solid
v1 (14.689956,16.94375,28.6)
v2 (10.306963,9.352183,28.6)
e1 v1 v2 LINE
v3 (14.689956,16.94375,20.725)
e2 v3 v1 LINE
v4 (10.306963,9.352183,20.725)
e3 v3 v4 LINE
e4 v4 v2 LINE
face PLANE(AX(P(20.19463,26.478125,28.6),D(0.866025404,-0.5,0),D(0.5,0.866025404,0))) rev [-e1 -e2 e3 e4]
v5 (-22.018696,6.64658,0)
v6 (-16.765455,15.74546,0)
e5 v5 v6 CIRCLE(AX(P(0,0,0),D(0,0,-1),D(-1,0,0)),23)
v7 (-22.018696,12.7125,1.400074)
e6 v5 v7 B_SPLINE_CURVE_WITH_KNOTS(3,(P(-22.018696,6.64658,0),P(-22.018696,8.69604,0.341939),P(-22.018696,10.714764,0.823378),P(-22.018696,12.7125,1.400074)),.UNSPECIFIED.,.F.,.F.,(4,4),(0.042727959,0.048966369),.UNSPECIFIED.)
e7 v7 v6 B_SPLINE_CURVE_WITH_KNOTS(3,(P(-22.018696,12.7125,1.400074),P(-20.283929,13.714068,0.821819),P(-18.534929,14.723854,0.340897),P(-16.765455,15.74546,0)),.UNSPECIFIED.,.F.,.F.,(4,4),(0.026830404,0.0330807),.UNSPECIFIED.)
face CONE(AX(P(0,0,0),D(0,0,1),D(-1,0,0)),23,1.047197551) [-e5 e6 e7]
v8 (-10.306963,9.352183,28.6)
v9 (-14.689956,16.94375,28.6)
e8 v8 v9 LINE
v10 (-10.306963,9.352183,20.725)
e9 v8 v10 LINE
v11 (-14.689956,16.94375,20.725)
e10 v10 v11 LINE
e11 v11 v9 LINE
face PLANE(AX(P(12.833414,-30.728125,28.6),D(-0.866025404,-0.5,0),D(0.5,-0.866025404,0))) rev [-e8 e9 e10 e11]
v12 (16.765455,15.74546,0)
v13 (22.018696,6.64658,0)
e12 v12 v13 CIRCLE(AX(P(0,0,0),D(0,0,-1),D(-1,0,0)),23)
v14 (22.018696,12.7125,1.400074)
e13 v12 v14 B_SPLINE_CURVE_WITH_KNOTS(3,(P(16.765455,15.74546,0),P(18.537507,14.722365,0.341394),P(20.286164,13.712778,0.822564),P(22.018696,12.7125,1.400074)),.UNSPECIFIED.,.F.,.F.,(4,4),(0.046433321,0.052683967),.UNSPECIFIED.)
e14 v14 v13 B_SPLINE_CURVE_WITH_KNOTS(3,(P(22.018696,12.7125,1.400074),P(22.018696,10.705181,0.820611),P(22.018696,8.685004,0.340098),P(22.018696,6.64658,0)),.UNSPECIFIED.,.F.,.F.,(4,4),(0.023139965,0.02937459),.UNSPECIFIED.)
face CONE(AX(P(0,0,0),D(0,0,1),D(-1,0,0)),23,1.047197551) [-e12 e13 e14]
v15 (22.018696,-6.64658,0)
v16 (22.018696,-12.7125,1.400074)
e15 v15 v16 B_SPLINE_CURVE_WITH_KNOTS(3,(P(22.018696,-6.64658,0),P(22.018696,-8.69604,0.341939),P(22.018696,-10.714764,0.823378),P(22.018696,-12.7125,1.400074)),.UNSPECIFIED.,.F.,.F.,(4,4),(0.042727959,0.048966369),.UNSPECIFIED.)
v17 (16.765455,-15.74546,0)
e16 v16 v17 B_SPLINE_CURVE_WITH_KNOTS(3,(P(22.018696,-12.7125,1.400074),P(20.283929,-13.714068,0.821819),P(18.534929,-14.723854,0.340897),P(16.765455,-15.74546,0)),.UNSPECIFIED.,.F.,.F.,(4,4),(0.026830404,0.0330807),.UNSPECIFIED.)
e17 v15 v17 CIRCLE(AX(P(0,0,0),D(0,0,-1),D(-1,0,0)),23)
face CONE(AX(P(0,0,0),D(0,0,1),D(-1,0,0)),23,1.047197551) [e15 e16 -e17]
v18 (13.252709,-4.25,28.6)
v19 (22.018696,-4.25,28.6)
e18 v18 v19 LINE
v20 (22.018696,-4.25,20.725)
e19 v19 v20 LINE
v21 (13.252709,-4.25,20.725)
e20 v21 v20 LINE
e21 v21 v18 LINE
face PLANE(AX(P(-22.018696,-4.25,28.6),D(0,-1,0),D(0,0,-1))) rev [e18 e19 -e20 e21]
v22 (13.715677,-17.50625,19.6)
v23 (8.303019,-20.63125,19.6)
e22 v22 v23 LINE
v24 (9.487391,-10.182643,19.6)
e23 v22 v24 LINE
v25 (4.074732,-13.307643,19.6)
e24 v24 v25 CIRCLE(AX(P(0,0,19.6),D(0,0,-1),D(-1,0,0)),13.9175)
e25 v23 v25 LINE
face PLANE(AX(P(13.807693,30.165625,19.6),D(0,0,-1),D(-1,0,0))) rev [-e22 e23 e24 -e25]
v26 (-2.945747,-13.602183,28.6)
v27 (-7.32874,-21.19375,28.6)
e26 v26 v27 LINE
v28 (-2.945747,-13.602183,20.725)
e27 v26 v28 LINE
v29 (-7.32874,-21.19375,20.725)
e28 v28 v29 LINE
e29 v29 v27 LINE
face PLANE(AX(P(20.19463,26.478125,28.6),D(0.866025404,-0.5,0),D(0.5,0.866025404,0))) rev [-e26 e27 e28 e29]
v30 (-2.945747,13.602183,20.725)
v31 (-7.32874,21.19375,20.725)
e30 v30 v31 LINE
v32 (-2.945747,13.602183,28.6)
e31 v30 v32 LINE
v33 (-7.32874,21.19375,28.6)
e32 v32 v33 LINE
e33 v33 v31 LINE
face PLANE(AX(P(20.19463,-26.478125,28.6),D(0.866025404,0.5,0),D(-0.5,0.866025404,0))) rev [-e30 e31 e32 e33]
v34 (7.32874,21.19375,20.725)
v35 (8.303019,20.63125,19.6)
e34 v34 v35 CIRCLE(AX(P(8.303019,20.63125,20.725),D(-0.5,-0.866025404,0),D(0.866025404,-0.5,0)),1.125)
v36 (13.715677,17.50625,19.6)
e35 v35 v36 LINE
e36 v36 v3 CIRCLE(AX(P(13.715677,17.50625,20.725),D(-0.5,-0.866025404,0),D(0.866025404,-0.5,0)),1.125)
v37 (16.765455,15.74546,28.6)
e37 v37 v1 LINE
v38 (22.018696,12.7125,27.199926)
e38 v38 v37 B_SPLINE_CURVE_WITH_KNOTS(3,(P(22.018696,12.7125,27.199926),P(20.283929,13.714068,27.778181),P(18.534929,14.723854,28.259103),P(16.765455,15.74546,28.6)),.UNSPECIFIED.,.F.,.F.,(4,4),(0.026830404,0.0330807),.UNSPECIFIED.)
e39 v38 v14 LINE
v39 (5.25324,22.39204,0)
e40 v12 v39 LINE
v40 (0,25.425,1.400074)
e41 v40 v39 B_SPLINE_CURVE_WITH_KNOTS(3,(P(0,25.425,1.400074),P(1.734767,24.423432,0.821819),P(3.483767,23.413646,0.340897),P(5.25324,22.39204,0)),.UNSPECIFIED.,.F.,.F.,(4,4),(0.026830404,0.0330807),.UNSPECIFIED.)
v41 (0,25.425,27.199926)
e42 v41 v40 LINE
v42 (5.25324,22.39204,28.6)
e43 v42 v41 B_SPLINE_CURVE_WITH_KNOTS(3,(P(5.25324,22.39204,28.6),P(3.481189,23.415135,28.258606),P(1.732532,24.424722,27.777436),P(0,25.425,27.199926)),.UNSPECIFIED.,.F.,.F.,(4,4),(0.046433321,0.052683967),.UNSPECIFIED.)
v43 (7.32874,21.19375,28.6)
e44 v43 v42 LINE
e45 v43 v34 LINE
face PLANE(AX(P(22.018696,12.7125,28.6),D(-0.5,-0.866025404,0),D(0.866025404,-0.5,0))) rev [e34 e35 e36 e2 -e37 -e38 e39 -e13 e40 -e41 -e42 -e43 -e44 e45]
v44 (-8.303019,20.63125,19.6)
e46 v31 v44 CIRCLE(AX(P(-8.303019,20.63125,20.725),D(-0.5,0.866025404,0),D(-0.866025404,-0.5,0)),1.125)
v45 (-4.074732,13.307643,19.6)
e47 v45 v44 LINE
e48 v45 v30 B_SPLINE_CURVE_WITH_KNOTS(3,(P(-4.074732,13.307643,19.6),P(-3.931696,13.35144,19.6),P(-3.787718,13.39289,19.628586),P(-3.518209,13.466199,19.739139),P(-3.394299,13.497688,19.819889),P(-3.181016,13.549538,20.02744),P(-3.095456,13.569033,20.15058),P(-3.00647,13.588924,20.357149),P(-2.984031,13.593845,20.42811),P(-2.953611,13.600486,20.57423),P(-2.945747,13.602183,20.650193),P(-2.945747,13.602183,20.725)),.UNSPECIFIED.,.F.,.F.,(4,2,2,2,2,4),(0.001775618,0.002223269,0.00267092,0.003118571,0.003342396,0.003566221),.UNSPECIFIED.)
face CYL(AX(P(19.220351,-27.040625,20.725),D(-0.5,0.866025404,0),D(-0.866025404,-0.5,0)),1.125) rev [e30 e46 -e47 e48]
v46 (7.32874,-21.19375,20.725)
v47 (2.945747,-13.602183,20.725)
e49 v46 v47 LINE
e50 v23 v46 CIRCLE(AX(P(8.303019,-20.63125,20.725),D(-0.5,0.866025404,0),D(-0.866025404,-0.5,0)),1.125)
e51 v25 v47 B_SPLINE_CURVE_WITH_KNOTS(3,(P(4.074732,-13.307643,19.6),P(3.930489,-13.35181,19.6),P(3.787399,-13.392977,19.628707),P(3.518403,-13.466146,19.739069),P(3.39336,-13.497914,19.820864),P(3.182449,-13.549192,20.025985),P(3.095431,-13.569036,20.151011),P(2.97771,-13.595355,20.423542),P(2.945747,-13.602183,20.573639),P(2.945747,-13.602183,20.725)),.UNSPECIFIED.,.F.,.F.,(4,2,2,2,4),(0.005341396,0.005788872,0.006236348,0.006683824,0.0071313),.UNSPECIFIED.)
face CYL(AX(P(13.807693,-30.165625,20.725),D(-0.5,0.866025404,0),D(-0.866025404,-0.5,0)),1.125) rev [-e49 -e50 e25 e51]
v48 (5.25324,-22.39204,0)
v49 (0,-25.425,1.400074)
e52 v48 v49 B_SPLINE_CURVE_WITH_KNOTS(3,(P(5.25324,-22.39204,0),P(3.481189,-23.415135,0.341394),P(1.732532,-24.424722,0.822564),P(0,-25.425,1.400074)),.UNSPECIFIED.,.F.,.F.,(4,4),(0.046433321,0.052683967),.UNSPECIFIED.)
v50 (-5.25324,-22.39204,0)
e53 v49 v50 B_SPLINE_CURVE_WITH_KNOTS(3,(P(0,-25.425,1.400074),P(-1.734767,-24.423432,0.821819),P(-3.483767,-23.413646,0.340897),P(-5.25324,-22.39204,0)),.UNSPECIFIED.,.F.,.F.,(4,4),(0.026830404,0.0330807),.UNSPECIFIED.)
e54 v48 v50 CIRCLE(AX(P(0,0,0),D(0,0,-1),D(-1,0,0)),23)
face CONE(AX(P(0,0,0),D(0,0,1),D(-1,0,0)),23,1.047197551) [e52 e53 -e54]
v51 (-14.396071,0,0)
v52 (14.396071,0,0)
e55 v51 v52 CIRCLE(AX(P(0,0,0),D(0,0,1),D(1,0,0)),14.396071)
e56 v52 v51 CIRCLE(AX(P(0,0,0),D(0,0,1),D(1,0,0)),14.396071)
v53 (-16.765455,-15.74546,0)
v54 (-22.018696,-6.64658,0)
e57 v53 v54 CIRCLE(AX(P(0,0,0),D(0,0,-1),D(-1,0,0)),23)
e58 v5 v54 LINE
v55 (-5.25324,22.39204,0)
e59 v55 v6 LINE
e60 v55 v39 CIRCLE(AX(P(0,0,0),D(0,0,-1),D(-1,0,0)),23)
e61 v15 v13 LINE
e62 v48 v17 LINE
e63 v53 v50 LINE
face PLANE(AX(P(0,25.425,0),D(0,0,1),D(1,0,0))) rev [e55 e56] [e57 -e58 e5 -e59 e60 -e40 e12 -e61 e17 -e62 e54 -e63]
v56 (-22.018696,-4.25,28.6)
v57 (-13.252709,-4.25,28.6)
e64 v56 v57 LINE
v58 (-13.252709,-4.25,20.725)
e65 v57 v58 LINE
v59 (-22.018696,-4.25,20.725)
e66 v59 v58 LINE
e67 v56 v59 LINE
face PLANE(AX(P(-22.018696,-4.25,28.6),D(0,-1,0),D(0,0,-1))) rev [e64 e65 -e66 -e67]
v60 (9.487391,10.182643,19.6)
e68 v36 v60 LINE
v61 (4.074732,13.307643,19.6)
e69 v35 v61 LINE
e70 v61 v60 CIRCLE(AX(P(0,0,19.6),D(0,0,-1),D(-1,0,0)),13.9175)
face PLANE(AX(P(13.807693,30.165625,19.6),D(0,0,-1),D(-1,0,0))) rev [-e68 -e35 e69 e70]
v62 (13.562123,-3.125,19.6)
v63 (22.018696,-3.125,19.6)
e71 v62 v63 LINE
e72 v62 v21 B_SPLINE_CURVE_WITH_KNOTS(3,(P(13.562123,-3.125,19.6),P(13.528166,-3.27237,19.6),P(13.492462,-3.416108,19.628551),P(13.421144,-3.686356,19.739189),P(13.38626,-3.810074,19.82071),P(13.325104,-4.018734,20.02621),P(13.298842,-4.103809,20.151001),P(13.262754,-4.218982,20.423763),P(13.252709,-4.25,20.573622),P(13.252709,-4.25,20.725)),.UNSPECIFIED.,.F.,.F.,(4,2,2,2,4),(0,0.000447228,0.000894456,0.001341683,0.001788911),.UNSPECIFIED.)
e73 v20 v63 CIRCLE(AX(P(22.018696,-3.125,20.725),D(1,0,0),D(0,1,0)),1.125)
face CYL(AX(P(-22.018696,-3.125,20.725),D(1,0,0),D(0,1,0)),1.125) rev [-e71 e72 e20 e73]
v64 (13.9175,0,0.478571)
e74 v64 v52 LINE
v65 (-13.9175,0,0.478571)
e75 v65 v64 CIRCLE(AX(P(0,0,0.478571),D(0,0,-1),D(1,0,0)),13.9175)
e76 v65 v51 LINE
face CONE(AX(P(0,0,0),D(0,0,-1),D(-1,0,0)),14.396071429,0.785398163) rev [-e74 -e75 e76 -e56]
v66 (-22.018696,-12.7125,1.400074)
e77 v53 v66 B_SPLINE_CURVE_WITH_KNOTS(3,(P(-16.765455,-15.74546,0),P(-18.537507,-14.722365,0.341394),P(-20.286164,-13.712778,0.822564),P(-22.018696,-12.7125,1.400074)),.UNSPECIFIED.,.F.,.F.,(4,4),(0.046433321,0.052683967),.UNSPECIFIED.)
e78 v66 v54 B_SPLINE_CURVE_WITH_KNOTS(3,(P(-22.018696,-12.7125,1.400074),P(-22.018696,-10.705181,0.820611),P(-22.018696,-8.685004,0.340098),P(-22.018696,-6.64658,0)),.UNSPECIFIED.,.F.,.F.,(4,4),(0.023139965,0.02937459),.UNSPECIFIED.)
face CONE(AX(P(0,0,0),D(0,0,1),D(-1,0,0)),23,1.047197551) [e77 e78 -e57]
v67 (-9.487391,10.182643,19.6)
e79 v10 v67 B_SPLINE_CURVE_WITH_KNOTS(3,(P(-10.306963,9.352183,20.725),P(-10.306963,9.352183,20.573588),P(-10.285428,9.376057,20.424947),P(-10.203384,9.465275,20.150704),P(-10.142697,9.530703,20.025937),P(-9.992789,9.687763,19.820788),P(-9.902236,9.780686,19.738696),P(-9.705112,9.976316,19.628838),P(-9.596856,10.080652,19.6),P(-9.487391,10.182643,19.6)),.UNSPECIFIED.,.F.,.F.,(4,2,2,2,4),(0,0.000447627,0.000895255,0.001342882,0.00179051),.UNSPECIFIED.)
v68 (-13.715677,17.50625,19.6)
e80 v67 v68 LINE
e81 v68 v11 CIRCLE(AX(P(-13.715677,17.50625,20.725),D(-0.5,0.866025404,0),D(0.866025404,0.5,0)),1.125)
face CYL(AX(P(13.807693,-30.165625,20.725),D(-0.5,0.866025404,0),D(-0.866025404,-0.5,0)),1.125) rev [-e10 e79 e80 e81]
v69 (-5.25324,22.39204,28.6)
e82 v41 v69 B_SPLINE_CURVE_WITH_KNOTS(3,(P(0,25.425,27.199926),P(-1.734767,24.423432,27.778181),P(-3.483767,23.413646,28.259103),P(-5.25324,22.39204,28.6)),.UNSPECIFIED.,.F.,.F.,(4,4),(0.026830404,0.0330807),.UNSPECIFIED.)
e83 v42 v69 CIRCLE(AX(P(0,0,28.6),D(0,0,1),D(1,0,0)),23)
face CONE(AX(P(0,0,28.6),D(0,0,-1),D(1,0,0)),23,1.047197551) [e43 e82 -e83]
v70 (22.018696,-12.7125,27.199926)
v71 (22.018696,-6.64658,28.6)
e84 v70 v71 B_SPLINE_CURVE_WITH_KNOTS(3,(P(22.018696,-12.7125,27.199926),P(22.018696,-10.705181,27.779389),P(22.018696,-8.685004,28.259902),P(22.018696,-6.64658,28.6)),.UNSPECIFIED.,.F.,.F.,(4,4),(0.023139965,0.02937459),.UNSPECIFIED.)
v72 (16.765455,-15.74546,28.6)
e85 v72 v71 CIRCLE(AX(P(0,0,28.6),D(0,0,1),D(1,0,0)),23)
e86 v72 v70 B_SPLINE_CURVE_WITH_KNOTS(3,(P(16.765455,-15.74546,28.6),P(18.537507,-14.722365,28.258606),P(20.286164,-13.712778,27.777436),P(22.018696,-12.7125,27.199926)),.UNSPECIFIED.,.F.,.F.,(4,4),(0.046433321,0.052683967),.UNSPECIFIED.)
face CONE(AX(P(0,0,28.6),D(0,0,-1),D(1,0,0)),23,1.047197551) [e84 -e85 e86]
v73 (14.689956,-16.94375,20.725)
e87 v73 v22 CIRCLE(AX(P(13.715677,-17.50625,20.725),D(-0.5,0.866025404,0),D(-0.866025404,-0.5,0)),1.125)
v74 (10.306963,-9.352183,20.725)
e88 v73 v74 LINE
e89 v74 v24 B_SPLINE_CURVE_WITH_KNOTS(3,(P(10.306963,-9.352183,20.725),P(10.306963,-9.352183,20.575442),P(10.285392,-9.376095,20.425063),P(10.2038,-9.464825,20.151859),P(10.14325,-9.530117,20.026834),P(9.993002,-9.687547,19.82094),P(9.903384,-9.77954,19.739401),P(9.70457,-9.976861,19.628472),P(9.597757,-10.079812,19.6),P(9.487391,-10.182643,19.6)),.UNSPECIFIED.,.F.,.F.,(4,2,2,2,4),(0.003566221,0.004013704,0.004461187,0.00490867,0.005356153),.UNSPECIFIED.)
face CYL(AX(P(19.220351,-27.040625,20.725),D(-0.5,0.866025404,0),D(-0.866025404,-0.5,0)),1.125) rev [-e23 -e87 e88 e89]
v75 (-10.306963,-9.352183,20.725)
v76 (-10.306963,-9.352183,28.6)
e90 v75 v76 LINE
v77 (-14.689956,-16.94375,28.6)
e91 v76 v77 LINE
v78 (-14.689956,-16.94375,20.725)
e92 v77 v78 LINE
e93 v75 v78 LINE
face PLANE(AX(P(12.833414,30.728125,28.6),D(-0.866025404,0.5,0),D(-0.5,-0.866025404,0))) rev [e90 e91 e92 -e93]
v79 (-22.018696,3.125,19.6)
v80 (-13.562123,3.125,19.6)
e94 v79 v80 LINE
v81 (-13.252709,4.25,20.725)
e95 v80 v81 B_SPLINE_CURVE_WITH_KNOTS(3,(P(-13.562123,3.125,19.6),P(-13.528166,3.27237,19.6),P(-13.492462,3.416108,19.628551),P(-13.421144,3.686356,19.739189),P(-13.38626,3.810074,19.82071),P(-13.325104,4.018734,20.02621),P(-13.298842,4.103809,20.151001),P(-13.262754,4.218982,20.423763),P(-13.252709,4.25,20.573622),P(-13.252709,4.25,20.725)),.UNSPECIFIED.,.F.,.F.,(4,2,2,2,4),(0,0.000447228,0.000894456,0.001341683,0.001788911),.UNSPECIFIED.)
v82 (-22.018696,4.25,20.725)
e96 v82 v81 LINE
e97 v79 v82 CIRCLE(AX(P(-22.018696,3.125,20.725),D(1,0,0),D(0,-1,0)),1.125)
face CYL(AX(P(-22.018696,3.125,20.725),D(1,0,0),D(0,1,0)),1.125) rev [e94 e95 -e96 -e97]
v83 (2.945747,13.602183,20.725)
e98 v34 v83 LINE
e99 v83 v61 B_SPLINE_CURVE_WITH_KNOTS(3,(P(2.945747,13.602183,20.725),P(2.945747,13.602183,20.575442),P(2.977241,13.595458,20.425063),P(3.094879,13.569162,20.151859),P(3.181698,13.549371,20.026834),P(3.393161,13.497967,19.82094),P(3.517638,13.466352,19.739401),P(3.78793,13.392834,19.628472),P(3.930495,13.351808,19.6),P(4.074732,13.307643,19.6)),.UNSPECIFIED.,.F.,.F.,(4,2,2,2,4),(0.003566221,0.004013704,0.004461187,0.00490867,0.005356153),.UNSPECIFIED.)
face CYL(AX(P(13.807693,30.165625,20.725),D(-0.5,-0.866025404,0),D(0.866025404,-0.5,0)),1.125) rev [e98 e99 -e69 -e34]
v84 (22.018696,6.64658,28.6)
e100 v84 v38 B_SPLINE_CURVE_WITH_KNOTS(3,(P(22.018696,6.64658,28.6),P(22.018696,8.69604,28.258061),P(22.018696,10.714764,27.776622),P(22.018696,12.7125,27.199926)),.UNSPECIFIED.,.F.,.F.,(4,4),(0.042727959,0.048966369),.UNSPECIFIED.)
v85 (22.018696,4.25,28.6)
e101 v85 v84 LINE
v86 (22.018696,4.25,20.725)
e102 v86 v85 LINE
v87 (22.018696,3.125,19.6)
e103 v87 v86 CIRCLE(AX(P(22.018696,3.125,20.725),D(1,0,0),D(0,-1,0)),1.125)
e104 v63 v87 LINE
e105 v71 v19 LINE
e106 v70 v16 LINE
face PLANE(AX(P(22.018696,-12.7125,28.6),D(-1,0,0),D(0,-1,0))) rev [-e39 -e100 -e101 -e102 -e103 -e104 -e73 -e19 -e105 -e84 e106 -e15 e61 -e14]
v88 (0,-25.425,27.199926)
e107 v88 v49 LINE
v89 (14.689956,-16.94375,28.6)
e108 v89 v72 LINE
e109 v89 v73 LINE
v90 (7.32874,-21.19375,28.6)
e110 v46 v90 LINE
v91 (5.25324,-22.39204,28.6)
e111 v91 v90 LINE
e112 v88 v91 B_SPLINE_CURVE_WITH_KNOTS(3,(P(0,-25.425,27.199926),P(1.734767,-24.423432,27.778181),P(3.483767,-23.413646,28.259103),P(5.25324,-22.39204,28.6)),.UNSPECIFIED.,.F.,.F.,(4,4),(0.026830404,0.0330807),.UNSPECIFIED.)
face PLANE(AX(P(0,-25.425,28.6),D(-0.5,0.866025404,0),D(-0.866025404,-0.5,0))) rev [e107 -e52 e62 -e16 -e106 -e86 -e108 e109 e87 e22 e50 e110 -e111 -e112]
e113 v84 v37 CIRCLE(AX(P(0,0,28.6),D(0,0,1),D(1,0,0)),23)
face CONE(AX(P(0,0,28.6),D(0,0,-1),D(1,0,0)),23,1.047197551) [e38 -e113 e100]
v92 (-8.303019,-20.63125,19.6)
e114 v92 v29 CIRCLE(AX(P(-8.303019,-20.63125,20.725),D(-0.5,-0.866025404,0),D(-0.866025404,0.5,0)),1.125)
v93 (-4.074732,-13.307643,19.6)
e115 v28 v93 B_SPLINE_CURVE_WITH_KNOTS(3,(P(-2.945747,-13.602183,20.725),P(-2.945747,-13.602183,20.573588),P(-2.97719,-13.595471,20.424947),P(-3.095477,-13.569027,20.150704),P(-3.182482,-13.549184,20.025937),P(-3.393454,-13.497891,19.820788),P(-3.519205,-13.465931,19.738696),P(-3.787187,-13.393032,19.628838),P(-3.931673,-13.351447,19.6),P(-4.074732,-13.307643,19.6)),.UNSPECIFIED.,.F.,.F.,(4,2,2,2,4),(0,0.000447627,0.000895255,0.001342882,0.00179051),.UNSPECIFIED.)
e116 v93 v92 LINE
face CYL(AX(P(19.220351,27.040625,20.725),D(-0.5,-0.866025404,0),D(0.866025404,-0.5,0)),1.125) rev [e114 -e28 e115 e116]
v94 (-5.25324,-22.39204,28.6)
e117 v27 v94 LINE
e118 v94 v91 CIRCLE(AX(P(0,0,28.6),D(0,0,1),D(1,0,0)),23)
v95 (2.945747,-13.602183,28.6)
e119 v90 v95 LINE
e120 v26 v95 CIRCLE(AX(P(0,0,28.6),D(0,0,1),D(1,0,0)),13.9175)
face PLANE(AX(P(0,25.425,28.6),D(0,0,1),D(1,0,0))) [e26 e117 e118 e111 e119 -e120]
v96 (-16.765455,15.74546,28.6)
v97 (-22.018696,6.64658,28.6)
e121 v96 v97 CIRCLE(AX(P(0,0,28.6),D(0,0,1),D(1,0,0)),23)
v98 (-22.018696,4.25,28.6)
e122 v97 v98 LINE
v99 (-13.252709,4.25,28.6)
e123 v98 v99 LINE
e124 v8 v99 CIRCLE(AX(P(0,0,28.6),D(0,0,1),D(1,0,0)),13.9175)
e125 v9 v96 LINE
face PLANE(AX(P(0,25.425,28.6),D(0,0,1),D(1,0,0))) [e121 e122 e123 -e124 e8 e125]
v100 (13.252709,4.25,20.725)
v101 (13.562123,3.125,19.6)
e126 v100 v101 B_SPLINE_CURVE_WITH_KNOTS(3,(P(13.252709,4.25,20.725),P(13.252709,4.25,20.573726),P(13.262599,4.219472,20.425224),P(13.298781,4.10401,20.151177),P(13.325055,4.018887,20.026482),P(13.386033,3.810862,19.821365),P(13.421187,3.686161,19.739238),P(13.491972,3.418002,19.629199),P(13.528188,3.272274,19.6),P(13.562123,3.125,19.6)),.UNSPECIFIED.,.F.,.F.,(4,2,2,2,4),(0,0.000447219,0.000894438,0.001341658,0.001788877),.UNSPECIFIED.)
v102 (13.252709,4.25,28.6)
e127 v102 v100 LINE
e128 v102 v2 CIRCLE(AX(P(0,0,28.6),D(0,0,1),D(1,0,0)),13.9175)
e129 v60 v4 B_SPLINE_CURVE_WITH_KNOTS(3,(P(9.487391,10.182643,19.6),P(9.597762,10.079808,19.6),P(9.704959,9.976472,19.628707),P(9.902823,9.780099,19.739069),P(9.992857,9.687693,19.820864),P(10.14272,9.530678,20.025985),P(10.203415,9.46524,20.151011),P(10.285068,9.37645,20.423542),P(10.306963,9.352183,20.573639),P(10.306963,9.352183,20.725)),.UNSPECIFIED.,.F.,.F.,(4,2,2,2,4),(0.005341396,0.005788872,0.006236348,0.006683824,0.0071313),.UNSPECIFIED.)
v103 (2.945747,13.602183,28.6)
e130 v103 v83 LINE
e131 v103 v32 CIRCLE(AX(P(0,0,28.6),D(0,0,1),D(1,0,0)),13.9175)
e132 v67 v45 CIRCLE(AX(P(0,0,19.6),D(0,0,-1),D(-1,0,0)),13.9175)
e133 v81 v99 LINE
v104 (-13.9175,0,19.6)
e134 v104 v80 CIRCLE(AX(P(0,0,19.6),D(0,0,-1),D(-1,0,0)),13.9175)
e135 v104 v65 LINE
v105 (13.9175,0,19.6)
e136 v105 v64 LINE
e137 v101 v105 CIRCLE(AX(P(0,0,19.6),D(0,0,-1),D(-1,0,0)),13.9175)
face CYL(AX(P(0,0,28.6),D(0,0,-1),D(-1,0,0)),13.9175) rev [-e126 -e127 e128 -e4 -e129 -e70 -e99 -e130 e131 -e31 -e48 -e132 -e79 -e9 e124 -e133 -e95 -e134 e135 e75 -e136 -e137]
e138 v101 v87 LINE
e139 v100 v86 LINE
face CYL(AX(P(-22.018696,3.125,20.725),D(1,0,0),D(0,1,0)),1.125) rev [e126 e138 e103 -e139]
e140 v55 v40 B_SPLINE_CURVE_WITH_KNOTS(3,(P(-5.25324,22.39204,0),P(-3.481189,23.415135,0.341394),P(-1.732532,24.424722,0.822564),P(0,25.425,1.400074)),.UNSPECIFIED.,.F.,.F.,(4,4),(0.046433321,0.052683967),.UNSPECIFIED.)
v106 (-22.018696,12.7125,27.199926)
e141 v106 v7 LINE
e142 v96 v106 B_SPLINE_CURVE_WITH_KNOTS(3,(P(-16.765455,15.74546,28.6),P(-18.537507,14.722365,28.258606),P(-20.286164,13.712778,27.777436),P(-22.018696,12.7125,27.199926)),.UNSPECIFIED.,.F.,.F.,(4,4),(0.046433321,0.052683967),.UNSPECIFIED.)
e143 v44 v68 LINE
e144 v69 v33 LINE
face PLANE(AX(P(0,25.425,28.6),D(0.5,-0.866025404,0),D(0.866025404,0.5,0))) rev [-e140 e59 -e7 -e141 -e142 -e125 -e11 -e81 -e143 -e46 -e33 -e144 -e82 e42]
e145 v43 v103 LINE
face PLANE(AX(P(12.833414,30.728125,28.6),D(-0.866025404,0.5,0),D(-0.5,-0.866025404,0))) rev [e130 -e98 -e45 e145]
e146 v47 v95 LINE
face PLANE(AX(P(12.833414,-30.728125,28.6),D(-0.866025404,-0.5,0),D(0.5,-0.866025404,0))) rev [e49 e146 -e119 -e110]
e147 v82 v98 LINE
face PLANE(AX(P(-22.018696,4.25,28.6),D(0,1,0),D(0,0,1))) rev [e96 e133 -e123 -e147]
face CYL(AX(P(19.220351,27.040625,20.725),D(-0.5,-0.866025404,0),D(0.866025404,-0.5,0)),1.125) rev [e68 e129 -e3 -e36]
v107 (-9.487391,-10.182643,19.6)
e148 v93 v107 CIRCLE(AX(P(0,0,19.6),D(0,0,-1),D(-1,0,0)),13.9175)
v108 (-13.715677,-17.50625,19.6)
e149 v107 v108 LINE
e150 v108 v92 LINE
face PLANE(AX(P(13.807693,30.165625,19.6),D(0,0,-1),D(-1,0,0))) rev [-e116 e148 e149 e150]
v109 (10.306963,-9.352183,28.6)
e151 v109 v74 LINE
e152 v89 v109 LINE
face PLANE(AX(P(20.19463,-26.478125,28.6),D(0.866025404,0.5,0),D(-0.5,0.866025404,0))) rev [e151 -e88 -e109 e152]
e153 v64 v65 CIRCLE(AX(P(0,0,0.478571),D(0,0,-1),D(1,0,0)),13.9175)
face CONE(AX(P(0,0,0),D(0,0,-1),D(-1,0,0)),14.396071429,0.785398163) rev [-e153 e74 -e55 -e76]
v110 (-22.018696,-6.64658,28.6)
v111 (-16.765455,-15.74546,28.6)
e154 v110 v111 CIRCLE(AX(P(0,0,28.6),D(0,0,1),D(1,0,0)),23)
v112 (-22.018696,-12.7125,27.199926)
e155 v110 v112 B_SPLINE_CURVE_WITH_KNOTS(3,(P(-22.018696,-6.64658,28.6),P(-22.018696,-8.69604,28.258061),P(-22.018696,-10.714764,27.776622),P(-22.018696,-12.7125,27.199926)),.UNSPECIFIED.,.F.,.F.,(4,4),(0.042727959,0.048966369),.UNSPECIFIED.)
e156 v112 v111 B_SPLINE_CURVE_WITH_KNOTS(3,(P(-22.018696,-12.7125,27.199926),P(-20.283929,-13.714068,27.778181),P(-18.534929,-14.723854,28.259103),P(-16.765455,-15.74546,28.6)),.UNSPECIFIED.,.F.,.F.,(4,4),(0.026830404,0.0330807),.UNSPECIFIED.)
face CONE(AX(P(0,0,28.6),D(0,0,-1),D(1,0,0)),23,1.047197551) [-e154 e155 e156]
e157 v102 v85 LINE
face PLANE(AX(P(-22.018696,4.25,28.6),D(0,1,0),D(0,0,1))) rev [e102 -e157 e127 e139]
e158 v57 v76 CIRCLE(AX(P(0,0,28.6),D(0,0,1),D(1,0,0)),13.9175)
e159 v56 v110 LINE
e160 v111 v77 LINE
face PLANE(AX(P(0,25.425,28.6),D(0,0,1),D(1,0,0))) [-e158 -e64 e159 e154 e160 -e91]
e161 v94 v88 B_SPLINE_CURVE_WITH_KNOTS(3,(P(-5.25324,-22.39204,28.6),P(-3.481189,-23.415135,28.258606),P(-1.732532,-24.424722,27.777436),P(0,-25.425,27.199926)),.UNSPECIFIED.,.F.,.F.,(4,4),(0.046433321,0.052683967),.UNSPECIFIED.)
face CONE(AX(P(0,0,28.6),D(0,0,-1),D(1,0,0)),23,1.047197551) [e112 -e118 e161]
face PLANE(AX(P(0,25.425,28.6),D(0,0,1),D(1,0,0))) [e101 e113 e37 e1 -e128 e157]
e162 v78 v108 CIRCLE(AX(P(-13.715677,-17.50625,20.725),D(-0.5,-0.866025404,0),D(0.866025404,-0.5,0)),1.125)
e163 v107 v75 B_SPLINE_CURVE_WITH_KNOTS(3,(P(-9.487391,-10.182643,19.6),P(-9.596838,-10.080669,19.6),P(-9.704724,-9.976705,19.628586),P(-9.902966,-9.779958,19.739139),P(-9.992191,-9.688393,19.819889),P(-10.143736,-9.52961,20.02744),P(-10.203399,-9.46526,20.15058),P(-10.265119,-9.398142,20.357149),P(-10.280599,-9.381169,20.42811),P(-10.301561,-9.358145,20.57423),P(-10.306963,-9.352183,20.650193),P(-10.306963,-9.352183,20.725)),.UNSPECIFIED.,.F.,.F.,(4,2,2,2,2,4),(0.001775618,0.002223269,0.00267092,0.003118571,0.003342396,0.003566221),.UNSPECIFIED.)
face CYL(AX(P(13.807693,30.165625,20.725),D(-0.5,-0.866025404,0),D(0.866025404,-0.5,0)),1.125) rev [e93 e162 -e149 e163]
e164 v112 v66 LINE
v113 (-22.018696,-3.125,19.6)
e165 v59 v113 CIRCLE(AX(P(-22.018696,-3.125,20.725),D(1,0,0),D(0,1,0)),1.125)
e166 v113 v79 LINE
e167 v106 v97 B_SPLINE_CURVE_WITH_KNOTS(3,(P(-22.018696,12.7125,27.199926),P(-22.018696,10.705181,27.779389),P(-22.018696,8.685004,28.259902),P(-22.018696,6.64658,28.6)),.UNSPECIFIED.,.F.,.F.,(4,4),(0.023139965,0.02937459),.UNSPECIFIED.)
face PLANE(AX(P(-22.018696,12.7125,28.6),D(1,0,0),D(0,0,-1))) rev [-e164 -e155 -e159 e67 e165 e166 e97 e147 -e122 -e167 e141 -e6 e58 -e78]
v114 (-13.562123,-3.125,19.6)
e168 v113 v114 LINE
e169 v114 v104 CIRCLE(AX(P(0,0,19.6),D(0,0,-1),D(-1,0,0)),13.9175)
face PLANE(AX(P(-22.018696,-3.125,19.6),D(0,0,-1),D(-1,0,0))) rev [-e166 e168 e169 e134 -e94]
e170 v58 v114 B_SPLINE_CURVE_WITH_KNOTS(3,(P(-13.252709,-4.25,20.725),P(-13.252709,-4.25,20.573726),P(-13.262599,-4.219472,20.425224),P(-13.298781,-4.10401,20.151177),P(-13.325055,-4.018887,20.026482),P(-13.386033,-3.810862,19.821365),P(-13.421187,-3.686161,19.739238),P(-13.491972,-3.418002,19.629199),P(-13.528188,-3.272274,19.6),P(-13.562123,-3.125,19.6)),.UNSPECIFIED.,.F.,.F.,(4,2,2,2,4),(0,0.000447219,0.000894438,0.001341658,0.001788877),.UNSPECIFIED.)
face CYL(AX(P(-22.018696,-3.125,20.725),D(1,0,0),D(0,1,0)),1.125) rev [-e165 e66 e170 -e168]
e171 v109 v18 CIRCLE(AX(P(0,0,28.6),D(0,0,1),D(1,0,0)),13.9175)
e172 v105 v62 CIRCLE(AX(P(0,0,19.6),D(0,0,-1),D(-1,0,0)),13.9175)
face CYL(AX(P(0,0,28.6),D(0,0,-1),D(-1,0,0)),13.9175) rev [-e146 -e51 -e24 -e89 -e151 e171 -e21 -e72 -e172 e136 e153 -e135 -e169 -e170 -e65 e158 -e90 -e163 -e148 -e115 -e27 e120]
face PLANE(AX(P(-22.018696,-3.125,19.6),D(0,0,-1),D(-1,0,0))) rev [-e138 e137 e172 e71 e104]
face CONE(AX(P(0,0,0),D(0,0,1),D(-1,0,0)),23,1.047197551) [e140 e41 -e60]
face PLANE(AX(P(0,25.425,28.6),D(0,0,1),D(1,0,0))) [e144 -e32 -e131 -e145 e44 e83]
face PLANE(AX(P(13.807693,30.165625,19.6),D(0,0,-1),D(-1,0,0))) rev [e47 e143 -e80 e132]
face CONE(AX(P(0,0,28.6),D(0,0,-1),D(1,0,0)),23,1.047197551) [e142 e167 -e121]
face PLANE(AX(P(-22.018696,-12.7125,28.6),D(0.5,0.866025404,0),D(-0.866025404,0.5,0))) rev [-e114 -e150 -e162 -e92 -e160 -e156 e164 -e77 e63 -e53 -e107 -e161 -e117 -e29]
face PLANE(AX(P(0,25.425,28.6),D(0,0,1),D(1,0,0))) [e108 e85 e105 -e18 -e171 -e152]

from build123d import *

# Parameters (mm, degrees)
SKETCH1_R          = 13.9175
BASE_EXTRUDE_DEPTH = 28.6
SKETCH2_OUTSIDE_W  = 217.06
SKETCH2_OUTSIDE_H  = 223.872
SKETCH2_OUTSIDE_R  = 23
CUT_EXTRUDE1_DEPTH = 45.149899136
CUT_EXTRUDE1_DRAFT = -60
SKETCH3_OUTSIDE_W  = 217.06
SKETCH3_OUTSIDE_H  = 223.872
SKETCH3_OUTSIDE_R  = 23
CUT_EXTRUDE2_DEPTH = 45.149899136
CUT_EXTRUDE2_DRAFT = -60
CUT_EXTRUDE3_DEPTH = 59.34108758
CIRPATTERN1_COUNT  = 3
CHAMFER1_SIZE      = 0.478571429


with BuildPart() as part:
    # Sketch1 → Base-Extrude (new body)
    with BuildSketch(Plane.XY):
        Polygon((0, 25.425), (-22.018695891, 12.7125), (-22.018695891, -12.7125), (0, -25.425), (22.018695891, -12.7125), (22.018695891, 12.7125), align=None)
        Circle(SKETCH1_R, mode=Mode.SUBTRACT)
    extrude(amount=BASE_EXTRUDE_DEPTH)


with BuildPart() as cut_extrude1_tool:
    # Sketch2 outside → Cut-Extrude1 (with draft: the straight prism first)
    with BuildSketch(Plane(origin=(0, 0, 0), x_dir=(-1, 0, 0), z_dir=(0, 0, -1))):
        Rectangle(SKETCH2_OUTSIDE_W, SKETCH2_OUTSIDE_H)
        Circle(SKETCH2_OUTSIDE_R, mode=Mode.SUBTRACT)
    extrude(amount=-CUT_EXTRUDE1_DEPTH)
    # Cut-Extrude1: the draft: its side faces are tilted about the plane it starts from
    cut_extrude1_sides = [cut_extrude1_tool.faces().sort_by_distance(p)[0] for p in [
        (0, -111.936, 22.574949568),
        (-108.53, 0, 22.574949568),
        (0, 111.936, 22.574949568),
        (108.53, 0, 22.574949568),
        (23, 0, 22.574949568),
    ]]
    draft(cut_extrude1_sides, Plane(origin=(0, 0, 0), x_dir=(-1, 0, 0), z_dir=(0, 0, -1)), CUT_EXTRUDE1_DRAFT)


with BuildPart() as part_1:
    add(part.part)

    # Cut-Extrude1: cut by cut_extrude1_tool
    add(cut_extrude1_tool.part, mode=Mode.SUBTRACT)


with BuildPart() as cut_extrude2_tool:
    # Sketch3 outside → Cut-Extrude2 (with draft: the straight prism first)
    with BuildSketch(Plane.XY.offset(28.6)):
        Rectangle(SKETCH3_OUTSIDE_W, SKETCH3_OUTSIDE_H)
        Circle(SKETCH3_OUTSIDE_R, mode=Mode.SUBTRACT)
    extrude(amount=-CUT_EXTRUDE2_DEPTH)
    # Cut-Extrude2: the draft: its side faces are tilted about the plane it starts from
    cut_extrude2_sides = [cut_extrude2_tool.faces().sort_by_distance(p)[0] for p in [
        (0, -111.936, 6.025050432),
        (108.53, 0, 6.025050432),
        (0, 111.936, 6.025050432),
        (-108.53, 0, 6.025050432),
        (-23, 0, 6.025050432),
    ]]
    draft(cut_extrude2_sides, Plane.XY.offset(28.6), CUT_EXTRUDE2_DRAFT)


with BuildPart() as part_2:
    add(part_1.part)

    # Cut-Extrude2: cut by cut_extrude2_tool
    add(cut_extrude2_tool.part, mode=Mode.SUBTRACT)

    # Sketch6 → Cut-Extrude3 (cut, through all)
    with BuildSketch(Plane(origin=(22.018695891, 0, 0), x_dir=(0, 0, -1), z_dir=(1, 0, 0))):
        with BuildLine():
            Line((-28.6, -4.25), (-28.6, 4.25))
            Line((-28.6, 4.25), (-20.725, 4.25))
            ThreePointArc((-20.725, 4.25), (-19.929504871, 3.920495129), (-19.6, 3.125))
            Line((-19.6, 3.125), (-19.6, -3.125))
            ThreePointArc((-19.6, -3.125), (-19.929504871, -3.920495129), (-20.725, -4.25))
            Line((-20.725, -4.25), (-28.6, -4.25))
        make_face()
    cut_extrude3 = extrude(amount=-CUT_EXTRUDE3_DEPTH, mode=Mode.SUBTRACT)

    # CirPattern1: Cut-Extrude3 ×3 about axis
    cirpattern1_axis = Axis((0, 0, 0), (0, 0, 1))
    for i in range(1, CIRPATTERN1_COUNT):
        add(cut_extrude3.rotate(cirpattern1_axis, i * 360 / CIRPATTERN1_COUNT), mode=Mode.SUBTRACT)

    # Chamfer1
    chamfer1_edges = [part_2.edges().sort_by_distance(p)[0] for p in [
        (-13.9175, 0, 0),
    ]]
    chamfer(chamfer1_edges, length=CHAMFER1_SIZE)


solid = part_2.part
